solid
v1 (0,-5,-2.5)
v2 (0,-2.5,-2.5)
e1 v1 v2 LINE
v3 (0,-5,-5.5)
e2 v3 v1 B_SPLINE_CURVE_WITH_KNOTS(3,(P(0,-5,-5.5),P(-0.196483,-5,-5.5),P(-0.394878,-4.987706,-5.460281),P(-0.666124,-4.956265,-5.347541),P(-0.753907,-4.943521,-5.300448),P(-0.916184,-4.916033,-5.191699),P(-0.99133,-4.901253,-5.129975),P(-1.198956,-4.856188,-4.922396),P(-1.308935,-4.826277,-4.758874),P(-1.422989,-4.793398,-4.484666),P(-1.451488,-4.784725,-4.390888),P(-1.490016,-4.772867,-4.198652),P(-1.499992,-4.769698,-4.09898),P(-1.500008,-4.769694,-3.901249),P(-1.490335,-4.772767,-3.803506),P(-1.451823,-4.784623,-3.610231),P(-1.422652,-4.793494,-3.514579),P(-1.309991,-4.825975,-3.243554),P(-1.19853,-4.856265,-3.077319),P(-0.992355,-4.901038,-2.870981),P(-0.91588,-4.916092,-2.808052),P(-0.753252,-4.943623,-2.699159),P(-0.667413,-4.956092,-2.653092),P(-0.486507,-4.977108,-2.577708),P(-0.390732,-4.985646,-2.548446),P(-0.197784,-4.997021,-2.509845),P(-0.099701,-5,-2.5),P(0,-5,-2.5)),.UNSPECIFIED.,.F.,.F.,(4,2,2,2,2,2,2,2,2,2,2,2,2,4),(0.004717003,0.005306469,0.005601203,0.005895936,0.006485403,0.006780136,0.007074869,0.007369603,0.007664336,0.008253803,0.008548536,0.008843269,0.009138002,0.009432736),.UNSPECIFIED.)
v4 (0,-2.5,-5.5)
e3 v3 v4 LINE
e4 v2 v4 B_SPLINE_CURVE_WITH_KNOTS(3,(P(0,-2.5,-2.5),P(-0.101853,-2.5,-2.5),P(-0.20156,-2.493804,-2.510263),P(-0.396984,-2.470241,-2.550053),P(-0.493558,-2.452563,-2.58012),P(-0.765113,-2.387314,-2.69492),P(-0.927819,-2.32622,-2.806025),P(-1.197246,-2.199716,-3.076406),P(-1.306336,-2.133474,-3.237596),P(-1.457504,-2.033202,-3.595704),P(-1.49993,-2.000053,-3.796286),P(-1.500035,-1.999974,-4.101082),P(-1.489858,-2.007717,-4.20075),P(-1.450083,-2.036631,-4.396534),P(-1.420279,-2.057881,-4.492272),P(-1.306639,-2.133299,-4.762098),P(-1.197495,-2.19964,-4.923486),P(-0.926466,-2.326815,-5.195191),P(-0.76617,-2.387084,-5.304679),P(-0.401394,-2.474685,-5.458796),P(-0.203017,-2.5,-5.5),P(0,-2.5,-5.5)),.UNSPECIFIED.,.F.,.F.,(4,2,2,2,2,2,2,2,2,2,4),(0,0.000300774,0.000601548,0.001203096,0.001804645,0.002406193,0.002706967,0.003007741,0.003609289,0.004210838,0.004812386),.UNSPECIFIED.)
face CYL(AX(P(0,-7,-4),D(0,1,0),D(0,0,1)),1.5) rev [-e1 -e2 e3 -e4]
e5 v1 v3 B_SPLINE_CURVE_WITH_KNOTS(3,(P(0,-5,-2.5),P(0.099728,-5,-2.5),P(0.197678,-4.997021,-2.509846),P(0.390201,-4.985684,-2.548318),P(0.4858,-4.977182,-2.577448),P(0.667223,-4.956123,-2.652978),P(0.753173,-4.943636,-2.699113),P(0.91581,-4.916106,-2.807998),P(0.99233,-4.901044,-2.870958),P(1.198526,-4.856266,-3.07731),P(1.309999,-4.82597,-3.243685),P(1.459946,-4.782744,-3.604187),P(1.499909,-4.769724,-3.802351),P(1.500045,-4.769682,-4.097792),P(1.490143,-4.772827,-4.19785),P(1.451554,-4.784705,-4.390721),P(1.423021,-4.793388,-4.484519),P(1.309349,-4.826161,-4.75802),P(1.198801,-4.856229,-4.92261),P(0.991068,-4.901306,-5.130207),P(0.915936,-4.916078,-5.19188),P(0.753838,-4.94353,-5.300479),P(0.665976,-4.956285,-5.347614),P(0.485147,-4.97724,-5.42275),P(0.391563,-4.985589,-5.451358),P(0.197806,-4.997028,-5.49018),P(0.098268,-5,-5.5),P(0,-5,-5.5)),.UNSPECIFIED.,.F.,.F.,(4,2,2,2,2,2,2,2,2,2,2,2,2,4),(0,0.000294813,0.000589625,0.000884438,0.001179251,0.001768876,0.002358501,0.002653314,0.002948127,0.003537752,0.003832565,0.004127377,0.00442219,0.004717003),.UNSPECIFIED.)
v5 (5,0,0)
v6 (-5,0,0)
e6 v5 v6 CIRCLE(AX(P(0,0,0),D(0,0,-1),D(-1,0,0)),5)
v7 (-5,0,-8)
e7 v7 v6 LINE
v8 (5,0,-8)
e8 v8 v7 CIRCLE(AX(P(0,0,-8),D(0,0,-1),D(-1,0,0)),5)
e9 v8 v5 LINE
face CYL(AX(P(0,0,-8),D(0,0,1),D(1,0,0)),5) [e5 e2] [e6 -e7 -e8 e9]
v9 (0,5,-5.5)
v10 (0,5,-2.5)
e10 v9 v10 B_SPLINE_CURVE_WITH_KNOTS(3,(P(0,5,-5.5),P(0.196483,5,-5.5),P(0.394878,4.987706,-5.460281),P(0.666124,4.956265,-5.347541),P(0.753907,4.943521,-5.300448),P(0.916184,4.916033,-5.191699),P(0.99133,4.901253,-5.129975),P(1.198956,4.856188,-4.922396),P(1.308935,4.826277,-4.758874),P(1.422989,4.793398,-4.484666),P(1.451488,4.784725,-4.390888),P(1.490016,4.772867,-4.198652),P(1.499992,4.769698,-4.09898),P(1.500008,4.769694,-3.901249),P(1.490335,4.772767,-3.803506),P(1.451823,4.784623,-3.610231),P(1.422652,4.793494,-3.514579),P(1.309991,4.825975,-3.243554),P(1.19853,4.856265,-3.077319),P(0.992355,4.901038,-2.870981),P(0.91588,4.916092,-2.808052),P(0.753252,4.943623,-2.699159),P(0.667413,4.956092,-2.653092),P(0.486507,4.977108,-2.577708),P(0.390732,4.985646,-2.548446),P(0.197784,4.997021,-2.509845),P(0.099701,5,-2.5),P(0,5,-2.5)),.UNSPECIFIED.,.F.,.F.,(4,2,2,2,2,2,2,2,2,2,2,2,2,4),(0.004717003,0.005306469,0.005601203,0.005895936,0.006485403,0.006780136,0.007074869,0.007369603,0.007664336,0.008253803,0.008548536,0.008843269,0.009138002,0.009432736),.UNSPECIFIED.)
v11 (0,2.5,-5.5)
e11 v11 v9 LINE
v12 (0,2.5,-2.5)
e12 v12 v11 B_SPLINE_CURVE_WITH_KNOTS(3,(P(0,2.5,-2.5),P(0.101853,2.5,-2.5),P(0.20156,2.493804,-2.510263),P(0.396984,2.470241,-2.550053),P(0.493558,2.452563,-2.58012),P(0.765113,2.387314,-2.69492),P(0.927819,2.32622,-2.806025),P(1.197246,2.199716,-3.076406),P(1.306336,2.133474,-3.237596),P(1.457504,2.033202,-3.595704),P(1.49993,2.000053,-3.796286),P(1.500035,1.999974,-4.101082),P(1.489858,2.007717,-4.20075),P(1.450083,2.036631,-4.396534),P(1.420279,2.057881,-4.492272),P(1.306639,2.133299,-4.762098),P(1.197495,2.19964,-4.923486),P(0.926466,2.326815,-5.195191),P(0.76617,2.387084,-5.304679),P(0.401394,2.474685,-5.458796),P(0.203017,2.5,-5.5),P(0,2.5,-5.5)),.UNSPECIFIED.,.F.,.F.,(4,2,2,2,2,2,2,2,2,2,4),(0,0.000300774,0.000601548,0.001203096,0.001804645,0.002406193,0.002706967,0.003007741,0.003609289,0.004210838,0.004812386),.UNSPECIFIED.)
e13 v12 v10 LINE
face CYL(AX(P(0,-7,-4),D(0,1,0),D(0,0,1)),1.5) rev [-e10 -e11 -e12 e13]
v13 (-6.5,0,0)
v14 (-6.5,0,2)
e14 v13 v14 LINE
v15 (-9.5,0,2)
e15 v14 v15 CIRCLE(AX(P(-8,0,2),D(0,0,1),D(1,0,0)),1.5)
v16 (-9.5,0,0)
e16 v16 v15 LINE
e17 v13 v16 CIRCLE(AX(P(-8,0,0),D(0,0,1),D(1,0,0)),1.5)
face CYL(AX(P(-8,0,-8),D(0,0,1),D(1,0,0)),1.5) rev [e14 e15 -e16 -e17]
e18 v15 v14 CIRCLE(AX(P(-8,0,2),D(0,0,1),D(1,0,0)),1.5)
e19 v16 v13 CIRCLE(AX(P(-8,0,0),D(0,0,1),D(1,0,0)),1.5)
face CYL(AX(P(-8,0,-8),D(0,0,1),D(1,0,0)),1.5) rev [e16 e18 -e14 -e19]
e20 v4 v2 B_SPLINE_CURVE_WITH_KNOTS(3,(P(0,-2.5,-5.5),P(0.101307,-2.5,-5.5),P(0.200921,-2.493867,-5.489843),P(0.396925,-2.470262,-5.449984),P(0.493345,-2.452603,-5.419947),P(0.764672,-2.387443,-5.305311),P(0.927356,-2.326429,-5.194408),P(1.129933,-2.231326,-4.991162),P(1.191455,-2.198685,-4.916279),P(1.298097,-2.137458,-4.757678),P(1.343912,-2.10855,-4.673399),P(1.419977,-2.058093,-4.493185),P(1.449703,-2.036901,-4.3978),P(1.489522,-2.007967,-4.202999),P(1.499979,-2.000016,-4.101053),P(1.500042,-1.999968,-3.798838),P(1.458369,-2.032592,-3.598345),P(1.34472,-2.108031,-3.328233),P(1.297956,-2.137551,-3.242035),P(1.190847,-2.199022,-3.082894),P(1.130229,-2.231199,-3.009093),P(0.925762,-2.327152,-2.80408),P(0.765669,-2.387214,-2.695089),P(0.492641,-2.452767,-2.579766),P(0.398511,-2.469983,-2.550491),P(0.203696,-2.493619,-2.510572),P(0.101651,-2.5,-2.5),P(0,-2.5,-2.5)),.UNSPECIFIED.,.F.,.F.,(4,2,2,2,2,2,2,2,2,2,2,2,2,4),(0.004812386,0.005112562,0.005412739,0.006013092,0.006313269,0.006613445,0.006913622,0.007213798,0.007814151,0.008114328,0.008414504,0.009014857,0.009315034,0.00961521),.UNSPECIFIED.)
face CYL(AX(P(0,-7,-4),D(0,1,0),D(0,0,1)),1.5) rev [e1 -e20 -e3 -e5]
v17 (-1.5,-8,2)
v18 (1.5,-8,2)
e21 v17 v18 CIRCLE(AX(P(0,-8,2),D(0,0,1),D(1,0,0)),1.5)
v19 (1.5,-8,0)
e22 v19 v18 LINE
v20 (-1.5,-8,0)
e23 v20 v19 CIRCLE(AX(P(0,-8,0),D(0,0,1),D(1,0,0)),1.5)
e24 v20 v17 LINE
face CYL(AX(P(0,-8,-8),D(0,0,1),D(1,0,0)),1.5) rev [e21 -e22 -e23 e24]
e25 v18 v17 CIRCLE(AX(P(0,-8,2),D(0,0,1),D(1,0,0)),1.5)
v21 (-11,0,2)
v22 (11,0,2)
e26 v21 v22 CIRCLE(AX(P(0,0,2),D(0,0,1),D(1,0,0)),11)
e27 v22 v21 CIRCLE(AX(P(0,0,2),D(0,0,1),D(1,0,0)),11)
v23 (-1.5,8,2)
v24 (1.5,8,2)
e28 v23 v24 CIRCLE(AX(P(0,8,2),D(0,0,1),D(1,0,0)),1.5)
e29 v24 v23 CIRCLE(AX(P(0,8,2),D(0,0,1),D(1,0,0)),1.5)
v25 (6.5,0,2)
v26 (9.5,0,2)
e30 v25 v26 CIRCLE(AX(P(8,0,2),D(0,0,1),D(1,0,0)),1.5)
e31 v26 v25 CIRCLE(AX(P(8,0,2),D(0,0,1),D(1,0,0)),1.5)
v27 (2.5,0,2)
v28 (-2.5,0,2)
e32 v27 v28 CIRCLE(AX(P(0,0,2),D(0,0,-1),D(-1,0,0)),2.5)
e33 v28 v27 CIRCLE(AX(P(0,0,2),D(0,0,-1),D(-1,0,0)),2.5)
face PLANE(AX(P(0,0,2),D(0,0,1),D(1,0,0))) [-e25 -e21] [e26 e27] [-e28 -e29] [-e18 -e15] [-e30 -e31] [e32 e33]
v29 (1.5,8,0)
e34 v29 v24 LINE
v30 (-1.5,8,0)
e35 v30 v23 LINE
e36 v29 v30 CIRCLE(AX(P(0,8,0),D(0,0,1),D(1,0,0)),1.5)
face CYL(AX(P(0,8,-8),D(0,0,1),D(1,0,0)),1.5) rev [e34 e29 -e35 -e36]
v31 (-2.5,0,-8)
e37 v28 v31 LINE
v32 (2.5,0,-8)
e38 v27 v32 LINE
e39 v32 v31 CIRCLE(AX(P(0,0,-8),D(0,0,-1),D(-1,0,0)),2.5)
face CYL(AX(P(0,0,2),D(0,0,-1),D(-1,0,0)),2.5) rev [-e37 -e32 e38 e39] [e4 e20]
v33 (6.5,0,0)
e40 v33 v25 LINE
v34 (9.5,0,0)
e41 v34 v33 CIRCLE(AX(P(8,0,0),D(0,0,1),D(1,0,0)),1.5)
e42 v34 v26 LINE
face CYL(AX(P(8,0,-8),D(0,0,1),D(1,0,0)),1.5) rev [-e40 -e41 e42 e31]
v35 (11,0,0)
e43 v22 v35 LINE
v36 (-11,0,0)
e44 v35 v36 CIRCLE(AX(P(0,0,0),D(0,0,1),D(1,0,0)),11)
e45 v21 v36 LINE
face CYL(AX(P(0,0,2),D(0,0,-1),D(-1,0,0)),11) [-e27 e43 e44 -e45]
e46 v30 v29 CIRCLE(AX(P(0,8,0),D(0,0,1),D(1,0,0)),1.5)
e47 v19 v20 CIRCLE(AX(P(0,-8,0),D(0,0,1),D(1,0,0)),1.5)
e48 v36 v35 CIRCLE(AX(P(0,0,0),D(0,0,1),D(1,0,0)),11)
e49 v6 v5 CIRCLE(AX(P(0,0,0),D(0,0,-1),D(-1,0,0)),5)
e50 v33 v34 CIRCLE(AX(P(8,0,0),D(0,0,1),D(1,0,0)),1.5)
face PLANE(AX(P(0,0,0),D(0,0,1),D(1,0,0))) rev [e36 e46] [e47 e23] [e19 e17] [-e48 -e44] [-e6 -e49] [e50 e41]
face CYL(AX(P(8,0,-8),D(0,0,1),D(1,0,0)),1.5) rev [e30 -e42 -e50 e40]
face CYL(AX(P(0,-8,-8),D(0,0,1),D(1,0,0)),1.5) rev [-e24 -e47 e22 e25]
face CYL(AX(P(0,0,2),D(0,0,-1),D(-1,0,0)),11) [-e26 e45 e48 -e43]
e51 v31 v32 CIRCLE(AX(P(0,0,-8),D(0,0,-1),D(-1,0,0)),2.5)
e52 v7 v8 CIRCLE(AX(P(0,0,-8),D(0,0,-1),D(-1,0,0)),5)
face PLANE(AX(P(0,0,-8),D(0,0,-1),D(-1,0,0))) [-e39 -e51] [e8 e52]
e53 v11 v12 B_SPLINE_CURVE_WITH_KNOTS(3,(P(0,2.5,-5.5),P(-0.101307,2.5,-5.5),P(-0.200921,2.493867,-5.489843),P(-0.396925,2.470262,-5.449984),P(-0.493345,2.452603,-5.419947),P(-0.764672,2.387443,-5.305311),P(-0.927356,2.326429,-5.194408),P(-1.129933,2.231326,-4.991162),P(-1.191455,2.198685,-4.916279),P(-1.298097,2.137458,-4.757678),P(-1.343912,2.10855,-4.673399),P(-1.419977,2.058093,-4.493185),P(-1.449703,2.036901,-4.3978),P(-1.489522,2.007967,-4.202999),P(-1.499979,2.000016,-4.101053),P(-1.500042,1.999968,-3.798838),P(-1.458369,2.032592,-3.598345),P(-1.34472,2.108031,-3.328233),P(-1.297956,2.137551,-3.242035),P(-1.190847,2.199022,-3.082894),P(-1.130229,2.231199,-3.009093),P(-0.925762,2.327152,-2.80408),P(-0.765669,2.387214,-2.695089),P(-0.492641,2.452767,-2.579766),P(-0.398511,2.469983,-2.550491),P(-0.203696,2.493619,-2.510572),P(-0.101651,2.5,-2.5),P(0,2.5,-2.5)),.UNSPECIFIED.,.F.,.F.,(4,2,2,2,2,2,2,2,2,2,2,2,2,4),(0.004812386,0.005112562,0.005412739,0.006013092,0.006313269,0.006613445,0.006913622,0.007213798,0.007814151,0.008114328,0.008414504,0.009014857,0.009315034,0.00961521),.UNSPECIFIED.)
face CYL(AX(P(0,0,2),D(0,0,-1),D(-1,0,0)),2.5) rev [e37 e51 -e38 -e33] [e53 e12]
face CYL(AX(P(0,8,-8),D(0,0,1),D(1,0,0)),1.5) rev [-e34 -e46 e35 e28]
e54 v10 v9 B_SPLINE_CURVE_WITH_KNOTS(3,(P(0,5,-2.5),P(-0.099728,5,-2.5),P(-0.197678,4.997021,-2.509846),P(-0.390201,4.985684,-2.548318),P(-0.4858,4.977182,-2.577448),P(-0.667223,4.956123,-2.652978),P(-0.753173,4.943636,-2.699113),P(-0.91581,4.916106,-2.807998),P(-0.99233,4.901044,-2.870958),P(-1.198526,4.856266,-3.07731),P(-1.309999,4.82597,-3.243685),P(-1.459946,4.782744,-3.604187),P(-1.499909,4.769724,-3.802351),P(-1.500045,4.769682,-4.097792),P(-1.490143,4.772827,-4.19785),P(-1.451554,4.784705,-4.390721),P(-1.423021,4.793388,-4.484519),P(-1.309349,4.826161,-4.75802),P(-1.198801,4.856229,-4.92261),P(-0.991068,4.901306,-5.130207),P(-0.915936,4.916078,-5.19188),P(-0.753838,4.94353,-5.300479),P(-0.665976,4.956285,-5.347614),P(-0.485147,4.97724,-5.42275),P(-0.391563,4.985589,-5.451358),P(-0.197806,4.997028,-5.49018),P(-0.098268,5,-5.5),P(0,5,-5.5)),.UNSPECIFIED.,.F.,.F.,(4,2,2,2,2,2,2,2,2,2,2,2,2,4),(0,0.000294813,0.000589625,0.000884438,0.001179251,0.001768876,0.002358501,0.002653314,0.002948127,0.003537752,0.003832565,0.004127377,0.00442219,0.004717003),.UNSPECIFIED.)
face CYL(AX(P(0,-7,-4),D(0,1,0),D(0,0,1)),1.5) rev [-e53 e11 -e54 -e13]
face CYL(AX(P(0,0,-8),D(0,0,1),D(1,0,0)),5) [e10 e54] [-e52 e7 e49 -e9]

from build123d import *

# Parameters (mm, degrees)
SKETCH1_R           = 11
BOSS_EXTRUDE1_DEPTH = 2
SKETCH2_R           = 5
BOSS_EXTRUDE2_DEPTH = 8
SKETCH3_R           = 2.5
CUT_EXTRUDE1_DEPTH  = 19.493242009
SKETCH4_R           = 1.5
CUT_EXTRUDE2_DEPTH  = 19.493242009
SKETCH5_R           = 1.5
CUT_EXTRUDE3_DEPTH  = 7


with BuildPart() as part:
    # Sketch1 → Boss-Extrude1 (new body)
    with BuildSketch(Plane.XY):
        Circle(SKETCH1_R)
    extrude(amount=BOSS_EXTRUDE1_DEPTH)

    # Sketch2 → Boss-Extrude2 (add)
    with BuildSketch(Plane(origin=(0, 0, 0), x_dir=(-1, 0, 0), z_dir=(0, 0, -1))):
        Circle(SKETCH2_R)
    extrude(amount=BOSS_EXTRUDE2_DEPTH)

    # Sketch3 → Cut-Extrude1 (cut, through all)
    with BuildSketch(Plane(origin=(0, 0, -8), x_dir=(-1, 0, 0), z_dir=(0, 0, -1))):
        Circle(SKETCH3_R)
    extrude(amount=-CUT_EXTRUDE1_DEPTH, mode=Mode.SUBTRACT)

    # Sketch4 → Cut-Extrude2 (cut, through all)
    with BuildSketch(Plane.XY.offset(2)):
        with Locations((0, -8)):
            Circle(SKETCH4_R)
        with Locations((-8, 0)):
            Circle(SKETCH4_R)
        with Locations((0, 8)):
            Circle(SKETCH4_R)
        with Locations((8, 0)):
            Circle(SKETCH4_R)
    extrude(amount=-CUT_EXTRUDE2_DEPTH, mode=Mode.SUBTRACT)

    # Sketch5 → Cut-Extrude3 (cut, symmetric)
    with BuildSketch(Plane(origin=(0, 0, 0), x_dir=(1, 0, 0), z_dir=(0, 1, 0))):
        with Locations(Location((0, 4, 0), (0, 0, 270))):
            Circle(SKETCH5_R)
    extrude(amount=CUT_EXTRUDE3_DEPTH, both=True, mode=Mode.SUBTRACT)


solid = part.part
